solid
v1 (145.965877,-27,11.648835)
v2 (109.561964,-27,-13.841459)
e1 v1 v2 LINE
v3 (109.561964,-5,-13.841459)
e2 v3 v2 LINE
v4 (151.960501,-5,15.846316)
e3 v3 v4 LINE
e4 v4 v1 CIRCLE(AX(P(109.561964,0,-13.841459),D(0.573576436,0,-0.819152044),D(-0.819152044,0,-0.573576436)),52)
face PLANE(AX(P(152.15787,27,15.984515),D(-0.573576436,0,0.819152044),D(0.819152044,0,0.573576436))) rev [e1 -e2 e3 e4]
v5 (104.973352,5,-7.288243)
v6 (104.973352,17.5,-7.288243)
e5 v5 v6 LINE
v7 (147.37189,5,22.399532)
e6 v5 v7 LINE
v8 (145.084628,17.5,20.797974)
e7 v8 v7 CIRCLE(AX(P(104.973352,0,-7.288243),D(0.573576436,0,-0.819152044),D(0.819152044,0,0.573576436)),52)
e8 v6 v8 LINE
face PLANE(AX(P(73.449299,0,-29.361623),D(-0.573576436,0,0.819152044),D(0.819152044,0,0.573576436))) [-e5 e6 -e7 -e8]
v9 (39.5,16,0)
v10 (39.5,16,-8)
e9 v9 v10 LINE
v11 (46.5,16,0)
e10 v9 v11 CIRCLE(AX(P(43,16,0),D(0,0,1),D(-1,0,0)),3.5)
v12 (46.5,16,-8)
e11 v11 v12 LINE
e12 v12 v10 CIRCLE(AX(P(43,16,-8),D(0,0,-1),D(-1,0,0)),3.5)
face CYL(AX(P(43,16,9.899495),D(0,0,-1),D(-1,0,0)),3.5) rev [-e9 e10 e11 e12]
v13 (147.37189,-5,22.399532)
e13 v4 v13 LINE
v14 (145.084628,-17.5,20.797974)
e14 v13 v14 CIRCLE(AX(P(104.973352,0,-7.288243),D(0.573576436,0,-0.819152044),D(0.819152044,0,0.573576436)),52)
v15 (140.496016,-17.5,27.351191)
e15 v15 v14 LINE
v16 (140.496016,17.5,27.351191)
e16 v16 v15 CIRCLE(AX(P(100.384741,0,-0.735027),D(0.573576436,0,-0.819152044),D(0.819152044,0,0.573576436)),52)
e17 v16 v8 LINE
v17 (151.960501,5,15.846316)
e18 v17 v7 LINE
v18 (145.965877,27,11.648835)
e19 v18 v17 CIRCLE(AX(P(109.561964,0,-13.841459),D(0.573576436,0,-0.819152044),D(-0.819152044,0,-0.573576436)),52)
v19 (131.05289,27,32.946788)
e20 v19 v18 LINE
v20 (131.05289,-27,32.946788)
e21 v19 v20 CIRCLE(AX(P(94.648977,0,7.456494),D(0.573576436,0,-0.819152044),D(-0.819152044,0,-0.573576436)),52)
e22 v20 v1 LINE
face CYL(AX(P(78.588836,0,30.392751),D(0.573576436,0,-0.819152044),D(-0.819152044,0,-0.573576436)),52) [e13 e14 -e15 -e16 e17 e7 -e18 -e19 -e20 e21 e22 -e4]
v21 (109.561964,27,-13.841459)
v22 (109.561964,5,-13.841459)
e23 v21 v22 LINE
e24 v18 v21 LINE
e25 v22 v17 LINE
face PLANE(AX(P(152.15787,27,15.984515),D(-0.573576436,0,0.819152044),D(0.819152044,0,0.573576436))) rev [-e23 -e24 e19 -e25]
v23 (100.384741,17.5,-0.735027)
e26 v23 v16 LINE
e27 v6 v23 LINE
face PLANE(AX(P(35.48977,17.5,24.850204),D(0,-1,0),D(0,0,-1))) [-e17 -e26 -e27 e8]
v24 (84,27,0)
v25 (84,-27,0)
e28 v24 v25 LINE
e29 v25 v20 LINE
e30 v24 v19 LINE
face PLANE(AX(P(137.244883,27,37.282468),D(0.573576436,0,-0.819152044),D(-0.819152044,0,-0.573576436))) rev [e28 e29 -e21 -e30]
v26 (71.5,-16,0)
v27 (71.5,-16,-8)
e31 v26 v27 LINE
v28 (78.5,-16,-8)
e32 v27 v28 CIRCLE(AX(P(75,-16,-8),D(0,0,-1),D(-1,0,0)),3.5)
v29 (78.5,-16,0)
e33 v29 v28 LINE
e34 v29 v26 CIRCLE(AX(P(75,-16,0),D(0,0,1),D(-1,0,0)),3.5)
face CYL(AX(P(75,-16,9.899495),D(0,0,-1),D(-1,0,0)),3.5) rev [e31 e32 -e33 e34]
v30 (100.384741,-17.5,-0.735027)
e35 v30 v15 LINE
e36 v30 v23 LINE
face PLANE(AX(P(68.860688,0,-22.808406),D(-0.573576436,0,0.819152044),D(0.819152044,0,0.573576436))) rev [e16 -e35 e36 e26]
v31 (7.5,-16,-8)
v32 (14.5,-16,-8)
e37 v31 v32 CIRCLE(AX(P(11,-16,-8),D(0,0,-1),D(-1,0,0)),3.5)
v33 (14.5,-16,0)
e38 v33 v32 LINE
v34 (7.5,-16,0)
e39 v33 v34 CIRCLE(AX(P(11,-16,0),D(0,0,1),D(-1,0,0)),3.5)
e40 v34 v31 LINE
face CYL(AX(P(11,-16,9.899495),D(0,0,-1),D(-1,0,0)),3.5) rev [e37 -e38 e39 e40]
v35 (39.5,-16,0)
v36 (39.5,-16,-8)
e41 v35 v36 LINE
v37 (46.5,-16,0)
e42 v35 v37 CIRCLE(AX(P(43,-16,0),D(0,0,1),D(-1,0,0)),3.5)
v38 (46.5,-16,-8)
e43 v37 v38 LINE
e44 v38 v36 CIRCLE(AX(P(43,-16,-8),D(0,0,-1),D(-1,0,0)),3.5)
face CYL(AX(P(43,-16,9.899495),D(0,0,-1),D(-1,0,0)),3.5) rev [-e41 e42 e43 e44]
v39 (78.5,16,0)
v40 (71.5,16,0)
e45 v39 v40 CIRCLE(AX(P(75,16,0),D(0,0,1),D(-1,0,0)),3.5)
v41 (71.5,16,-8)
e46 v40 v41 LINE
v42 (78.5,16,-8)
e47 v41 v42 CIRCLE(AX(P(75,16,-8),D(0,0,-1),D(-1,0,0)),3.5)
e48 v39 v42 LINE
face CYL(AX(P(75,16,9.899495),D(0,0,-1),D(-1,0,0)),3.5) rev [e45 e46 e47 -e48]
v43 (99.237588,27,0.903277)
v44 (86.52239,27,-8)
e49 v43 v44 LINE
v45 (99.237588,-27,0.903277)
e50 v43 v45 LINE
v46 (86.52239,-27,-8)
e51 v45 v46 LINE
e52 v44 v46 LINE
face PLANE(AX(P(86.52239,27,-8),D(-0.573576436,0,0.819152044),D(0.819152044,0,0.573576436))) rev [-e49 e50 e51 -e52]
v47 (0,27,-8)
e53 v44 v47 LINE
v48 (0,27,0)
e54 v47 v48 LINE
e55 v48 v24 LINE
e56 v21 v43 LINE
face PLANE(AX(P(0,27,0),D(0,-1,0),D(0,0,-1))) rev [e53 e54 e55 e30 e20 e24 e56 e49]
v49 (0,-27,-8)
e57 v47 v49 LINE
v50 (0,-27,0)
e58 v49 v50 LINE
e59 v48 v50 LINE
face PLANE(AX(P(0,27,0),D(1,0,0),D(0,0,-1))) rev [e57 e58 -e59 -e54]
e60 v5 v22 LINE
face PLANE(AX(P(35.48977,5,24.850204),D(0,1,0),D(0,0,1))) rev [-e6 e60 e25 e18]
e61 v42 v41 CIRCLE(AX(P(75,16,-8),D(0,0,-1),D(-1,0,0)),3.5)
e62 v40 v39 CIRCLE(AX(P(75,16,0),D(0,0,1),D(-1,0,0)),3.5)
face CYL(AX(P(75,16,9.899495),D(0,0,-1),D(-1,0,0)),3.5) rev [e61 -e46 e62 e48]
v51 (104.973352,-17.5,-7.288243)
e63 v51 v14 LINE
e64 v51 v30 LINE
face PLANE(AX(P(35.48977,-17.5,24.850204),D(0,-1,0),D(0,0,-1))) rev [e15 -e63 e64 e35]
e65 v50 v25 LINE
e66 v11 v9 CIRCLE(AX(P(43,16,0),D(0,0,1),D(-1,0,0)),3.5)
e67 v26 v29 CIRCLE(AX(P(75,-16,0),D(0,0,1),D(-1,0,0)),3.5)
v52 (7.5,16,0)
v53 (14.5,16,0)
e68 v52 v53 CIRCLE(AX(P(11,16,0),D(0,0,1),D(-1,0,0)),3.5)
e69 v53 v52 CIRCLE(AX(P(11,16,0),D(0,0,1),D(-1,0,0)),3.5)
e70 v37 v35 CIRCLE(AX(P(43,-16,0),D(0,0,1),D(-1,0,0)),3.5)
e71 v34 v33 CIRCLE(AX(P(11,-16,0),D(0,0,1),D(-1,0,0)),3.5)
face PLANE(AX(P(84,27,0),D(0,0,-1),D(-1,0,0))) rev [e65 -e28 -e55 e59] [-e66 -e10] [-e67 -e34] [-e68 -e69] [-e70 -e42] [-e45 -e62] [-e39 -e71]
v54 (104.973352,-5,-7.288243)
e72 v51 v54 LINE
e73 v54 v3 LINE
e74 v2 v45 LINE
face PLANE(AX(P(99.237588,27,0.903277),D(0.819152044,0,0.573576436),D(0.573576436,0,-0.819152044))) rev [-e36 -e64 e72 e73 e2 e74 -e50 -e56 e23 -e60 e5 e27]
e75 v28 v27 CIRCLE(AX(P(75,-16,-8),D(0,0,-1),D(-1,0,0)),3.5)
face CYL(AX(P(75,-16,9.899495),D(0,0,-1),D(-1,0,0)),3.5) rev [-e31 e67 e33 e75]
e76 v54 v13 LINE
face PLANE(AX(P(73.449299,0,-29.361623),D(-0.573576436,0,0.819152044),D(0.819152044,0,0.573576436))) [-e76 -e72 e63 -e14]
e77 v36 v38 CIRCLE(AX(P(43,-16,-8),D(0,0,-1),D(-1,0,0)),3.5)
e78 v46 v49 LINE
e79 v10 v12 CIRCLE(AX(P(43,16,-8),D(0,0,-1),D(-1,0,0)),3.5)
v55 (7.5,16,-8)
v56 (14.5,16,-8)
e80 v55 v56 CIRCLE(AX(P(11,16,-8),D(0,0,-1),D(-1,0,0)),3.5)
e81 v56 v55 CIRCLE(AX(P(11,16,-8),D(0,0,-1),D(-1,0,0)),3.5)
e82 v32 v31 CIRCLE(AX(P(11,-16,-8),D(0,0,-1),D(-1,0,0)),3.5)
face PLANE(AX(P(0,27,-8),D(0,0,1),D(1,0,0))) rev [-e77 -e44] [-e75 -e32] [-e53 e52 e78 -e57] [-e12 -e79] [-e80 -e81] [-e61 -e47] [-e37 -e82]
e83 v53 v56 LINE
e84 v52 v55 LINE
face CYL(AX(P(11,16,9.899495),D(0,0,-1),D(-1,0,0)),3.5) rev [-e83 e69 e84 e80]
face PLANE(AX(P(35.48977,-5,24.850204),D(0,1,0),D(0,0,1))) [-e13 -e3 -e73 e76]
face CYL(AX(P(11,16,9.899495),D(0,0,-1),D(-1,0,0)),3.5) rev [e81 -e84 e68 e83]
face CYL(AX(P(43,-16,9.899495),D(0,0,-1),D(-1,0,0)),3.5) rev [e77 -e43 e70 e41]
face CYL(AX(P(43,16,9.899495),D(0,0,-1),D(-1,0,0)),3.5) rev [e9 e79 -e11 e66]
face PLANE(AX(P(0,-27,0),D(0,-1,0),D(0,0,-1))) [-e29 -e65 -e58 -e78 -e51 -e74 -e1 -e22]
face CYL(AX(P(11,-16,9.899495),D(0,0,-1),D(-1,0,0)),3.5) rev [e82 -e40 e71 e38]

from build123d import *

# Parameters (mm, degrees)
BRACKET_BODY_DEPTH        = 27
PROFILE_TRIM_CUT_DEPTH    = 54
END_SLOT_CUT_DEPTH        = 60
MOUNTING_HOLES_SKETCH_R   = 3.5
MOUNTING_HOLES_6X_7_DEPTH = 8


with BuildPart() as part:
    # Bracket Profile Sketch → Bracket Body (new, symmetric)
    with BuildSketch(Plane(origin=(0, 0, 0), x_dir=(1, 0, 0), z_dir=(0, 1, 0))):
        Polygon((0, 0), (0, 8), (86.522390311, 8), (99.237588067, -0.903277318), (109.561963921, 13.841459479), (152.157870224, -15.984515211), (137.244882879, -37.282468363), (84, 0), align=None)
    extrude(amount=BRACKET_BODY_DEPTH, both=True)

    # Profile Trim Sketch → Profile Trim Cut (cut)
    with BuildSketch(Plane(origin=(42.548141325, 0, -60.765043225), x_dir=(-0.819152044288991, 0, -0.5735764363510474), z_dir=(0.5735764363510474, 0, -0.819152044288991))):
        with BuildLine():
            ThreePointArc((-133.80877172, 1.36e-07), (-131.883368797, 14.019084406), (-126.249743807, 27))
            Line((-126.249743807, 27), (-133.80877172, 27))
            Line((-133.80877172, 27), (-133.80877172, 1.36e-07))
        make_face()
        with BuildLine():
            ThreePointArc((-126.249743807, -27), (-131.883368834, -14.019084275), (-133.80877172, 1.36e-07))
            Line((-133.80877172, 1.36e-07), (-133.80877172, -27))
            Line((-133.80877172, -27), (-126.249743807, -27))
        make_face()
    extrude(amount=-PROFILE_TRIM_CUT_DEPTH, mode=Mode.SUBTRACT)

    # End Slot Sketch → End Slot Cut (cut)
    with BuildSketch(Plane(origin=(116.162945253, 0, 81.338169927), x_dir=(-0.5735764363510482, 0, 0.8191520442889904), z_dir=(-0.8191520442889904, 0, -0.5735764363510482))):
        Polygon((-74.180420653, 5), (-66.180420653, 5), (-66.180420653, 17.5), (-58.180420653, 17.5), (-58.180420653, -17.5), (-66.180420653, -17.5), (-66.180420653, -5), (-74.180420653, -5), align=None)
    extrude(amount=END_SLOT_CUT_DEPTH, mode=Mode.SUBTRACT)

    # Mounting Holes Sketch → Mounting Holes 6xØ7 (cut)
    with BuildSketch(Plane(origin=(0, 0, -8), x_dir=(-1, 0, 0), z_dir=(0, 0, -1))):
        with Locations((-11, 16)):
            Circle(MOUNTING_HOLES_SKETCH_R)
        with Locations((-11, -16)):
            Circle(MOUNTING_HOLES_SKETCH_R)
        with Locations((-43, 16)):
            Circle(MOUNTING_HOLES_SKETCH_R)
        with Locations((-43, -16)):
            Circle(MOUNTING_HOLES_SKETCH_R)
        with Locations((-75, 16)):
            Circle(MOUNTING_HOLES_SKETCH_R)
        with Locations((-75, -16)):
            Circle(MOUNTING_HOLES_SKETCH_R)
    extrude(amount=-MOUNTING_HOLES_6X_7_DEPTH, mode=Mode.SUBTRACT)


solid = part.part
